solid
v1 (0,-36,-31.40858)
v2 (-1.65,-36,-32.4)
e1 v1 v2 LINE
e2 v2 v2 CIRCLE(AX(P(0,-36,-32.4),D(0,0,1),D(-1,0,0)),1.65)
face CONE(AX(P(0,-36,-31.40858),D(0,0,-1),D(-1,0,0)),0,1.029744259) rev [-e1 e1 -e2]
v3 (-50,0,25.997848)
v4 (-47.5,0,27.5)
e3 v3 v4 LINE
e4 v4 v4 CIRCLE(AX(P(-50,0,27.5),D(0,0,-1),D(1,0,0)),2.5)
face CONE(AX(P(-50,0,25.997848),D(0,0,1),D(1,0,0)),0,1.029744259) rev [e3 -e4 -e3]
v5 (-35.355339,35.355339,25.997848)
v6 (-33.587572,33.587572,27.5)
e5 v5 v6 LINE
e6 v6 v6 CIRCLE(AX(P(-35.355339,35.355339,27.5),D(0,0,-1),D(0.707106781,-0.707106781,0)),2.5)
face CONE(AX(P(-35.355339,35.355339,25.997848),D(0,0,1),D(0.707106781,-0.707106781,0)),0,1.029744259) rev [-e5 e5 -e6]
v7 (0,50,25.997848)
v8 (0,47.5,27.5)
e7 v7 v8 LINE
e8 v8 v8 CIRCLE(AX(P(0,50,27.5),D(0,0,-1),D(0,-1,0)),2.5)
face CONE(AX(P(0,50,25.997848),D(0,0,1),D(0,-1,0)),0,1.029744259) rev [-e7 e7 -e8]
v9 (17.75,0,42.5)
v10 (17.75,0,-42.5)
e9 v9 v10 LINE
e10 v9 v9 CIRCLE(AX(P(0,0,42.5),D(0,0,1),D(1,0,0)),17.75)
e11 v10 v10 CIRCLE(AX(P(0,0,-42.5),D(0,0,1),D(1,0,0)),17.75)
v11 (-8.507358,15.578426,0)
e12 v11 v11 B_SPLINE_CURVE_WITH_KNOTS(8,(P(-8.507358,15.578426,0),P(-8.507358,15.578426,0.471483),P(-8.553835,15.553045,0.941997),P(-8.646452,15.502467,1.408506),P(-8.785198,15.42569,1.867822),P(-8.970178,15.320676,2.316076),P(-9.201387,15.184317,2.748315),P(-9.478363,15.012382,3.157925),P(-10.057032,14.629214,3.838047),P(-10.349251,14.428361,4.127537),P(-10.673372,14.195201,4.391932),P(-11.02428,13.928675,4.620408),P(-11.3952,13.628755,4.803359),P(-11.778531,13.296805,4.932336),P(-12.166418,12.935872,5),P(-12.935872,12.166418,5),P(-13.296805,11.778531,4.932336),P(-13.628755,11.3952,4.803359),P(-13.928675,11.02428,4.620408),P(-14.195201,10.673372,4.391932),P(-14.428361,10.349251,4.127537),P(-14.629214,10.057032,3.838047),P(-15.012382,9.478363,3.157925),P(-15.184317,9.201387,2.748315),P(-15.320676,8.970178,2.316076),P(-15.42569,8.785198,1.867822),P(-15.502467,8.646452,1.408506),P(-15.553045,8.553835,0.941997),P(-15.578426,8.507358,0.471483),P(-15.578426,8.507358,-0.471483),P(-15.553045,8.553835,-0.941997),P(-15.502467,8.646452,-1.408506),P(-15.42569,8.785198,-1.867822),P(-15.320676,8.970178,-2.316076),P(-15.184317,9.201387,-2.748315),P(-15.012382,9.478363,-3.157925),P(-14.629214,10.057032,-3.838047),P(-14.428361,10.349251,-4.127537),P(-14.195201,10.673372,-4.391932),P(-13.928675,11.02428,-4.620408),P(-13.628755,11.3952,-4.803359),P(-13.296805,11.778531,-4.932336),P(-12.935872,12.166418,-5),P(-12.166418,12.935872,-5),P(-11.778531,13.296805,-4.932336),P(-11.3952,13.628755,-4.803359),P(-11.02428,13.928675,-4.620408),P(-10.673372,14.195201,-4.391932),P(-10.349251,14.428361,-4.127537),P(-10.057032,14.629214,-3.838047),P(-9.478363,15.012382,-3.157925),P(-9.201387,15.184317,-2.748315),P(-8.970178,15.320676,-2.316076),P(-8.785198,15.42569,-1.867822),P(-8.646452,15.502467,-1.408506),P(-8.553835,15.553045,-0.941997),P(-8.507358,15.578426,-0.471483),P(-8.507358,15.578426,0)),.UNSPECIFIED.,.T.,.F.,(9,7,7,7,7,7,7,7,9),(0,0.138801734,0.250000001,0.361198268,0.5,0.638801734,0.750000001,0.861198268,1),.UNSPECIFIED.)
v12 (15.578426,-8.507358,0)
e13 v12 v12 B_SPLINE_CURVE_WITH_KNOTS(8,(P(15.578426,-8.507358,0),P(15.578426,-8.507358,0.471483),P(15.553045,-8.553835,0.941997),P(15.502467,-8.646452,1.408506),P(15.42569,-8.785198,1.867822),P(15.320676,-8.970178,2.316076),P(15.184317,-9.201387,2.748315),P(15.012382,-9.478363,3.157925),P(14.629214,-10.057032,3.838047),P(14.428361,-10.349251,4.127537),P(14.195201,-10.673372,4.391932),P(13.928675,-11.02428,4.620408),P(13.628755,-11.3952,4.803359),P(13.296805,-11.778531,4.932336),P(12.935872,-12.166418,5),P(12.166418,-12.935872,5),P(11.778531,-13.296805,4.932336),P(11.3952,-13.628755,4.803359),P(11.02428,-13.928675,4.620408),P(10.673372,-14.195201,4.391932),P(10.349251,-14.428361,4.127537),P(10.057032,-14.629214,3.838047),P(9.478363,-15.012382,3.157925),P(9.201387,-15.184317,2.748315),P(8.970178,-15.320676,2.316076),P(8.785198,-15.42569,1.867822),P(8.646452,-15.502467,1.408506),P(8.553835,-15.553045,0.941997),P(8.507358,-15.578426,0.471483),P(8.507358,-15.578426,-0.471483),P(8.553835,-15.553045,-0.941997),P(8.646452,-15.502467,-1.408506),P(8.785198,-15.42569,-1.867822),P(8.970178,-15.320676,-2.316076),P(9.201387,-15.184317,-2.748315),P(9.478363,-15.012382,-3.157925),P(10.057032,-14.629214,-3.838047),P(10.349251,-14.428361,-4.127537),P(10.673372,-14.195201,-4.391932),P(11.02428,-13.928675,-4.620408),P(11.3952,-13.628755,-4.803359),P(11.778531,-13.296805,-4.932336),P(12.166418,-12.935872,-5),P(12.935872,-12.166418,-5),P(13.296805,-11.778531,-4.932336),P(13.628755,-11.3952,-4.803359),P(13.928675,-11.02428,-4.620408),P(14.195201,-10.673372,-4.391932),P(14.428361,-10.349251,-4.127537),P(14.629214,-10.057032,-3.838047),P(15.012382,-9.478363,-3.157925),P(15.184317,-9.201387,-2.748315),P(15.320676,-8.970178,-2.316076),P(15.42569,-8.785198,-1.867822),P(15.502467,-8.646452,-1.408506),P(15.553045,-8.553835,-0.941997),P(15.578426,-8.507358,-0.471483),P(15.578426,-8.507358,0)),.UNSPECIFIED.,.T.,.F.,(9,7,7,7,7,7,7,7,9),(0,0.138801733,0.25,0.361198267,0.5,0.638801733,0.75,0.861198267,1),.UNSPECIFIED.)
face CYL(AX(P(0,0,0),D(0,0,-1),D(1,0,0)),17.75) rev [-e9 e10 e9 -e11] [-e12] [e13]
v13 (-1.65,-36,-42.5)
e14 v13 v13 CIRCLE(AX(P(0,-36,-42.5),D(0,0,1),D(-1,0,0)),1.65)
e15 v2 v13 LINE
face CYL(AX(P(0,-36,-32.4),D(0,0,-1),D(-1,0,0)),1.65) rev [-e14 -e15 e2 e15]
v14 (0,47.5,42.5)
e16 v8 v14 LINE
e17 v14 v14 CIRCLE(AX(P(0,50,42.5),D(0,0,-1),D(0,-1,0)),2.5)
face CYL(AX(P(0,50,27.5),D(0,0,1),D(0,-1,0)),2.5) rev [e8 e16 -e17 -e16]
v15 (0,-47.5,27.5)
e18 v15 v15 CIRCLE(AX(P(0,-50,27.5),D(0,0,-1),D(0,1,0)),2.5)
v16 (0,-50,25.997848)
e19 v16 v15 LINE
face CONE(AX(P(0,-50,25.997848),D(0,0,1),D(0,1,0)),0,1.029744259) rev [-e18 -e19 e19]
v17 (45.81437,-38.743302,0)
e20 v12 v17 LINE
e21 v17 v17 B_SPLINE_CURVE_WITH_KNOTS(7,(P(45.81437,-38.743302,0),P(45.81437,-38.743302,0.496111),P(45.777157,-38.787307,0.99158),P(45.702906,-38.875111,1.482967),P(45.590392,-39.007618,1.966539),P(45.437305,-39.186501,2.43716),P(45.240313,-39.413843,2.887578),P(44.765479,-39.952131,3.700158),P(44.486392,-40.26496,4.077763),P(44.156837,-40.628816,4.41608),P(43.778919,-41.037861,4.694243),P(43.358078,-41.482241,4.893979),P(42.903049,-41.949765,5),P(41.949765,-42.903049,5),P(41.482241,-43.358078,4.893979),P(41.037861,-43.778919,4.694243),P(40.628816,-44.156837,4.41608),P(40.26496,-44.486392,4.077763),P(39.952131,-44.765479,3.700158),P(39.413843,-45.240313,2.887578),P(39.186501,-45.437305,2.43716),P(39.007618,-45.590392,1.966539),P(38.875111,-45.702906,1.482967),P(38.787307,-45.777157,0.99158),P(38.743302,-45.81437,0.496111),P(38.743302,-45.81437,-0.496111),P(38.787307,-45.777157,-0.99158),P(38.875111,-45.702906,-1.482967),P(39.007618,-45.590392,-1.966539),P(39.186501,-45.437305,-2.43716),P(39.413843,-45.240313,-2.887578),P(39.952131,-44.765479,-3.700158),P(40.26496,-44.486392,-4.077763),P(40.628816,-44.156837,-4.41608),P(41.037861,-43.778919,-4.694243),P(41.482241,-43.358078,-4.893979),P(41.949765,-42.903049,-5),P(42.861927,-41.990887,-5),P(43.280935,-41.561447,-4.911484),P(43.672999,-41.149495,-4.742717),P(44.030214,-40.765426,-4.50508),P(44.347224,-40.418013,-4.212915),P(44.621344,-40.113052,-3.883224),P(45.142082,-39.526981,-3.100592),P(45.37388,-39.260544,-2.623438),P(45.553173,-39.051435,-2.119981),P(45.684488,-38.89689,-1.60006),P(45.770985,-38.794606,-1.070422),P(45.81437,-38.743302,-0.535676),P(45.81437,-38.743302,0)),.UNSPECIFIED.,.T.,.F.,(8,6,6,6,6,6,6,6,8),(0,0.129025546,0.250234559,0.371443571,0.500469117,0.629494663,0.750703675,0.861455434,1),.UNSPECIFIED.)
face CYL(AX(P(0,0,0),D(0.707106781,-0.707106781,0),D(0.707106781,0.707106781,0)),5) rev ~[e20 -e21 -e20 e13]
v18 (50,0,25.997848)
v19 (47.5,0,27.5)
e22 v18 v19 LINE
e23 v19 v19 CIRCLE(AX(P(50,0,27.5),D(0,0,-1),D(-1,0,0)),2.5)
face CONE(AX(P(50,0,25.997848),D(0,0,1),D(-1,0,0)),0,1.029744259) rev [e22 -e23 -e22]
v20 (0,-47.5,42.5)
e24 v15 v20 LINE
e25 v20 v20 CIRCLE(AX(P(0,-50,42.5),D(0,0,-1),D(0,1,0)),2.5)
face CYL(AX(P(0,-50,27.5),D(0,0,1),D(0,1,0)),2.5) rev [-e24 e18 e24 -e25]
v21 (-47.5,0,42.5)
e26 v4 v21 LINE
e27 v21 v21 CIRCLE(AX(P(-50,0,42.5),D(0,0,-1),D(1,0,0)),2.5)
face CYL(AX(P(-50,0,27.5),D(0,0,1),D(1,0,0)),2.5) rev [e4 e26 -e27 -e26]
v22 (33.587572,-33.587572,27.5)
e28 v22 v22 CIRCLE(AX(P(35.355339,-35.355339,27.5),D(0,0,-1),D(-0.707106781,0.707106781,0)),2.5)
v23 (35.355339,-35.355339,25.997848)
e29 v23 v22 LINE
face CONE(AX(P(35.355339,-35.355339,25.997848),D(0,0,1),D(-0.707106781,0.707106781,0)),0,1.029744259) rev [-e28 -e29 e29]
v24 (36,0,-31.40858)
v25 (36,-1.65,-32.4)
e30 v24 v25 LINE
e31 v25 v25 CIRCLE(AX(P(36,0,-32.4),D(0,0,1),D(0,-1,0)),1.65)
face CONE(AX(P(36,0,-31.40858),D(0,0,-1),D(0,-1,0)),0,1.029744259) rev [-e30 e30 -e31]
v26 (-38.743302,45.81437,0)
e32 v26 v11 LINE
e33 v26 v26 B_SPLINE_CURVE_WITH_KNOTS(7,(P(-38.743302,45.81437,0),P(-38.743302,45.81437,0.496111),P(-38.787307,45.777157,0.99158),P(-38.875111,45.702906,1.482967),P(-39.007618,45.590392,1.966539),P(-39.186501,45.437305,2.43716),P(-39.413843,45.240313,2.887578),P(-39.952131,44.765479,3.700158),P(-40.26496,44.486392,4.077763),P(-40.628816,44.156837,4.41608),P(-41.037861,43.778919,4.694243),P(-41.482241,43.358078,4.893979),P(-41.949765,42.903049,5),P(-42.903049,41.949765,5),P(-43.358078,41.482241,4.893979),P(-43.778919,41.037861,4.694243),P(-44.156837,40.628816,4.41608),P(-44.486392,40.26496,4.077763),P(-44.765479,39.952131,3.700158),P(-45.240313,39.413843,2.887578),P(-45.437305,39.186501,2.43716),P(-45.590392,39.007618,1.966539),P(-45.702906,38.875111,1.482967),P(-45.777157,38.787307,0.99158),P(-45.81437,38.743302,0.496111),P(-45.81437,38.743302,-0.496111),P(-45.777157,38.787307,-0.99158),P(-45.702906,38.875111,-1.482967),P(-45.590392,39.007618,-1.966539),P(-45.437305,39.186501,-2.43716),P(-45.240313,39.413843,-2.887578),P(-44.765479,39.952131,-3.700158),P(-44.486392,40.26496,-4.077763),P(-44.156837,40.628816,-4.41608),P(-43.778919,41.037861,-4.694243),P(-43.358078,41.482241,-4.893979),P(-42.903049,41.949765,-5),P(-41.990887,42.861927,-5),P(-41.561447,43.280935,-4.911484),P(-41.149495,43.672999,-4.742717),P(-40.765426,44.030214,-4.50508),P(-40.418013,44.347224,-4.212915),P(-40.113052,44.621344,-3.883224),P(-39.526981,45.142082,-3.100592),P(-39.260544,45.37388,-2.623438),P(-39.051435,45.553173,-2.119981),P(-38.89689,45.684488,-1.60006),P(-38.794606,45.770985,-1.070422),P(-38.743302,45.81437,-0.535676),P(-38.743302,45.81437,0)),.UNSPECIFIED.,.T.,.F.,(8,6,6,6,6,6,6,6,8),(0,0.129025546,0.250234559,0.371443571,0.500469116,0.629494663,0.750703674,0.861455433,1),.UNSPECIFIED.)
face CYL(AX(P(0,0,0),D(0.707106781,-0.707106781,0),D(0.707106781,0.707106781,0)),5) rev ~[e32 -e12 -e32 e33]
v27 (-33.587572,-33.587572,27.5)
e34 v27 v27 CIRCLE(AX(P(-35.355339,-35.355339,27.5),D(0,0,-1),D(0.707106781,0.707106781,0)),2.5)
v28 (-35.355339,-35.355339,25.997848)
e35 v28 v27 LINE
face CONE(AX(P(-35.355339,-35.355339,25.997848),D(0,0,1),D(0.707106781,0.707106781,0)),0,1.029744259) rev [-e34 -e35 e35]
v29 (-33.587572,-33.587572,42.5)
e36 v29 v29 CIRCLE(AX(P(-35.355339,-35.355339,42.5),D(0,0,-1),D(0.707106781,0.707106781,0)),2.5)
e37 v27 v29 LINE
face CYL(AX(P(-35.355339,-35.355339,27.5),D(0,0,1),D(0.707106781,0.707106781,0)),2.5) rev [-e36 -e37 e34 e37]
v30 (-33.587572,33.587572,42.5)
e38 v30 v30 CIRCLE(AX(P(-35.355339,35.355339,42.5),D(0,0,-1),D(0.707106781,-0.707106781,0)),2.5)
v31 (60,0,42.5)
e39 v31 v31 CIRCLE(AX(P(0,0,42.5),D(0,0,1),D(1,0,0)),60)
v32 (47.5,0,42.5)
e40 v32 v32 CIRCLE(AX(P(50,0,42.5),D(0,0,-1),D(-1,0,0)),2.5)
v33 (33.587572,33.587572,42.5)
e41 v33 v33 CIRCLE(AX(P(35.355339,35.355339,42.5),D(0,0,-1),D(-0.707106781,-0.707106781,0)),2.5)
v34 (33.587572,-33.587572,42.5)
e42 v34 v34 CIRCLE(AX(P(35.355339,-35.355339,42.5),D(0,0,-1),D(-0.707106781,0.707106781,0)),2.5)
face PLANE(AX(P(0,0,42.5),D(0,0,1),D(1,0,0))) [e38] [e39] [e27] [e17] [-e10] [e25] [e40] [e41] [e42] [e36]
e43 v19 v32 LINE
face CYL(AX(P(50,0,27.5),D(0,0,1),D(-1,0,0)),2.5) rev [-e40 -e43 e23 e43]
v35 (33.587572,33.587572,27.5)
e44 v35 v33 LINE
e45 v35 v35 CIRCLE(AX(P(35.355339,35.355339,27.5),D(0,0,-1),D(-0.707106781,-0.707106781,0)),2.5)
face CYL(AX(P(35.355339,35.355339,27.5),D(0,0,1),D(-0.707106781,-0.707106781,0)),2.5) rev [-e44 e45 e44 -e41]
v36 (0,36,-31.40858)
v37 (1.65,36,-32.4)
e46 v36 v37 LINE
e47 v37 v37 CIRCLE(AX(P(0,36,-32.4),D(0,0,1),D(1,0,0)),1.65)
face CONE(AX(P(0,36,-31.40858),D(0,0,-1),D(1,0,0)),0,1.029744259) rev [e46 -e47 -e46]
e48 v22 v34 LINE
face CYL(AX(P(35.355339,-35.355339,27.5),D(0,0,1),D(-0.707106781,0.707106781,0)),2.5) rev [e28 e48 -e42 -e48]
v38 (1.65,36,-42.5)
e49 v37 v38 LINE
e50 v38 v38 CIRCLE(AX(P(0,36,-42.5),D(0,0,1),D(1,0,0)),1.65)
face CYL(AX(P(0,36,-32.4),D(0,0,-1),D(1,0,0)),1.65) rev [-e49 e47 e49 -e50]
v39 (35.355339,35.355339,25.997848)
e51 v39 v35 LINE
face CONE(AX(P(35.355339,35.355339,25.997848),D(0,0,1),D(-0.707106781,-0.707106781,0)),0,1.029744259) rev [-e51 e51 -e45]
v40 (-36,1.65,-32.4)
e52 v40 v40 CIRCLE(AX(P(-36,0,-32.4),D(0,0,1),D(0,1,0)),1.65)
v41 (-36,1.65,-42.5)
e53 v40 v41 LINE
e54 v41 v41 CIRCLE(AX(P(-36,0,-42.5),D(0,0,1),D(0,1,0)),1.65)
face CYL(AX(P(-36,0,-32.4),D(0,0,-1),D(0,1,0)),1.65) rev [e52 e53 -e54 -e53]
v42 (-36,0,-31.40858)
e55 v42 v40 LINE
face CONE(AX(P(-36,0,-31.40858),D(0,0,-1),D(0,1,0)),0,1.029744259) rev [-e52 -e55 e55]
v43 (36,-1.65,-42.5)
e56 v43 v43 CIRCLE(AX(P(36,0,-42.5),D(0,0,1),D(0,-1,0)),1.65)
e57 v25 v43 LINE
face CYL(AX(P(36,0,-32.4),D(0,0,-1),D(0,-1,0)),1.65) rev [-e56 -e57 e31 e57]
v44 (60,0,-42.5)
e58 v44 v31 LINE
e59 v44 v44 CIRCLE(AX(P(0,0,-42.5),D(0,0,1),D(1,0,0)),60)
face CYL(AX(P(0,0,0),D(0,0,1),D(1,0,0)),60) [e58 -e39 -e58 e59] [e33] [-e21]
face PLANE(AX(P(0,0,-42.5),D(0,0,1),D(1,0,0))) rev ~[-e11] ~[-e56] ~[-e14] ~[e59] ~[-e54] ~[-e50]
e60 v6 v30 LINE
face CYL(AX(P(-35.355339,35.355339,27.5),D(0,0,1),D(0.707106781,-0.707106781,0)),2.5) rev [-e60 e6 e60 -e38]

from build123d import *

# Parameters (mm, degrees)
SKETCH_1_R               = 60
SKETCH_1_R_2             = 17.75
EXTRUDE_1_DEPTH          = 42.5
PATTERN_CIRCULAR_1_COUNT = 8
PATTERN_CIRCULAR_2_COUNT = 4
SKETCH_6_R               = 5
CUT_EXTRUDE_1_DEPTH      = 90


with BuildPart() as part:
    # 草图1 → 凸台-拉伸1 (new, symmetric)
    with BuildSketch(Plane.XY):
        Circle(SKETCH_1_R)
        Circle(SKETCH_1_R_2, mode=Mode.SUBTRACT)
    extrude(amount=EXTRUDE_1_DEPTH, both=True)

    # 草图3 → M6x1.0 螺纹孔1 (revolve, cut)
    with BuildSketch(Plane(origin=(0, 50, 42.5), x_dir=(0, -1, 0), z_dir=(1, 0, 0))):
        Polygon((0, 0), (0, 16.502151548), (2.5, 15), (2.5, 0), align=None)
    m6x1_0_1 = revolve(axis=Axis((0, 50, 48.85), (0, 0, -1)), mode=Mode.SUBTRACT)

    # 阵列(圆周)1: M6x1.0 螺纹孔1 ×8 about axis
    pattern_circular_1_axis = Axis((0, 0, 0), (0, 0, 1))
    for i in range(1, PATTERN_CIRCULAR_1_COUNT):
        add(m6x1_0_1.rotate(pattern_circular_1_axis, i * 360 / PATTERN_CIRCULAR_1_COUNT), mode=Mode.SUBTRACT)

    # 草图5 → M4x0.7 螺纹孔1 (revolve, cut)
    with BuildSketch(Plane(origin=(-36, 0, -42.5), x_dir=(0, 1, 0), z_dir=(1, 0, 0))):
        Polygon((0, 0), (0, 11.091420021), (1.65, 10.1), (1.65, 0), align=None)
    m4x0_7_1 = revolve(axis=Axis((-36, 0, -48.85), (0, 0, 1)), mode=Mode.SUBTRACT)

    # 阵列(圆周)2: M4x0.7 螺纹孔1 ×4 about axis
    pattern_circular_2_axis = Axis((0, 0, 0), (0, 0, 1))
    for i in range(1, PATTERN_CIRCULAR_2_COUNT):
        add(m4x0_7_1.rotate(pattern_circular_2_axis, i * 360 / PATTERN_CIRCULAR_2_COUNT), mode=Mode.SUBTRACT)

    # 草图6 → 切除-拉伸1 (cut, symmetric)
    with BuildSketch(Plane(origin=(0, 0, 0), x_dir=(-0.7071067811865438, -0.7071067811865512, 0), z_dir=(0.7071067811865512, -0.7071067811865438, 0))):
        with Locations(Location((0, 0, 0), (0, 0, 180))):
            Circle(SKETCH_6_R)
    extrude(amount=CUT_EXTRUDE_1_DEPTH, both=True, mode=Mode.SUBTRACT)


solid = part.part
